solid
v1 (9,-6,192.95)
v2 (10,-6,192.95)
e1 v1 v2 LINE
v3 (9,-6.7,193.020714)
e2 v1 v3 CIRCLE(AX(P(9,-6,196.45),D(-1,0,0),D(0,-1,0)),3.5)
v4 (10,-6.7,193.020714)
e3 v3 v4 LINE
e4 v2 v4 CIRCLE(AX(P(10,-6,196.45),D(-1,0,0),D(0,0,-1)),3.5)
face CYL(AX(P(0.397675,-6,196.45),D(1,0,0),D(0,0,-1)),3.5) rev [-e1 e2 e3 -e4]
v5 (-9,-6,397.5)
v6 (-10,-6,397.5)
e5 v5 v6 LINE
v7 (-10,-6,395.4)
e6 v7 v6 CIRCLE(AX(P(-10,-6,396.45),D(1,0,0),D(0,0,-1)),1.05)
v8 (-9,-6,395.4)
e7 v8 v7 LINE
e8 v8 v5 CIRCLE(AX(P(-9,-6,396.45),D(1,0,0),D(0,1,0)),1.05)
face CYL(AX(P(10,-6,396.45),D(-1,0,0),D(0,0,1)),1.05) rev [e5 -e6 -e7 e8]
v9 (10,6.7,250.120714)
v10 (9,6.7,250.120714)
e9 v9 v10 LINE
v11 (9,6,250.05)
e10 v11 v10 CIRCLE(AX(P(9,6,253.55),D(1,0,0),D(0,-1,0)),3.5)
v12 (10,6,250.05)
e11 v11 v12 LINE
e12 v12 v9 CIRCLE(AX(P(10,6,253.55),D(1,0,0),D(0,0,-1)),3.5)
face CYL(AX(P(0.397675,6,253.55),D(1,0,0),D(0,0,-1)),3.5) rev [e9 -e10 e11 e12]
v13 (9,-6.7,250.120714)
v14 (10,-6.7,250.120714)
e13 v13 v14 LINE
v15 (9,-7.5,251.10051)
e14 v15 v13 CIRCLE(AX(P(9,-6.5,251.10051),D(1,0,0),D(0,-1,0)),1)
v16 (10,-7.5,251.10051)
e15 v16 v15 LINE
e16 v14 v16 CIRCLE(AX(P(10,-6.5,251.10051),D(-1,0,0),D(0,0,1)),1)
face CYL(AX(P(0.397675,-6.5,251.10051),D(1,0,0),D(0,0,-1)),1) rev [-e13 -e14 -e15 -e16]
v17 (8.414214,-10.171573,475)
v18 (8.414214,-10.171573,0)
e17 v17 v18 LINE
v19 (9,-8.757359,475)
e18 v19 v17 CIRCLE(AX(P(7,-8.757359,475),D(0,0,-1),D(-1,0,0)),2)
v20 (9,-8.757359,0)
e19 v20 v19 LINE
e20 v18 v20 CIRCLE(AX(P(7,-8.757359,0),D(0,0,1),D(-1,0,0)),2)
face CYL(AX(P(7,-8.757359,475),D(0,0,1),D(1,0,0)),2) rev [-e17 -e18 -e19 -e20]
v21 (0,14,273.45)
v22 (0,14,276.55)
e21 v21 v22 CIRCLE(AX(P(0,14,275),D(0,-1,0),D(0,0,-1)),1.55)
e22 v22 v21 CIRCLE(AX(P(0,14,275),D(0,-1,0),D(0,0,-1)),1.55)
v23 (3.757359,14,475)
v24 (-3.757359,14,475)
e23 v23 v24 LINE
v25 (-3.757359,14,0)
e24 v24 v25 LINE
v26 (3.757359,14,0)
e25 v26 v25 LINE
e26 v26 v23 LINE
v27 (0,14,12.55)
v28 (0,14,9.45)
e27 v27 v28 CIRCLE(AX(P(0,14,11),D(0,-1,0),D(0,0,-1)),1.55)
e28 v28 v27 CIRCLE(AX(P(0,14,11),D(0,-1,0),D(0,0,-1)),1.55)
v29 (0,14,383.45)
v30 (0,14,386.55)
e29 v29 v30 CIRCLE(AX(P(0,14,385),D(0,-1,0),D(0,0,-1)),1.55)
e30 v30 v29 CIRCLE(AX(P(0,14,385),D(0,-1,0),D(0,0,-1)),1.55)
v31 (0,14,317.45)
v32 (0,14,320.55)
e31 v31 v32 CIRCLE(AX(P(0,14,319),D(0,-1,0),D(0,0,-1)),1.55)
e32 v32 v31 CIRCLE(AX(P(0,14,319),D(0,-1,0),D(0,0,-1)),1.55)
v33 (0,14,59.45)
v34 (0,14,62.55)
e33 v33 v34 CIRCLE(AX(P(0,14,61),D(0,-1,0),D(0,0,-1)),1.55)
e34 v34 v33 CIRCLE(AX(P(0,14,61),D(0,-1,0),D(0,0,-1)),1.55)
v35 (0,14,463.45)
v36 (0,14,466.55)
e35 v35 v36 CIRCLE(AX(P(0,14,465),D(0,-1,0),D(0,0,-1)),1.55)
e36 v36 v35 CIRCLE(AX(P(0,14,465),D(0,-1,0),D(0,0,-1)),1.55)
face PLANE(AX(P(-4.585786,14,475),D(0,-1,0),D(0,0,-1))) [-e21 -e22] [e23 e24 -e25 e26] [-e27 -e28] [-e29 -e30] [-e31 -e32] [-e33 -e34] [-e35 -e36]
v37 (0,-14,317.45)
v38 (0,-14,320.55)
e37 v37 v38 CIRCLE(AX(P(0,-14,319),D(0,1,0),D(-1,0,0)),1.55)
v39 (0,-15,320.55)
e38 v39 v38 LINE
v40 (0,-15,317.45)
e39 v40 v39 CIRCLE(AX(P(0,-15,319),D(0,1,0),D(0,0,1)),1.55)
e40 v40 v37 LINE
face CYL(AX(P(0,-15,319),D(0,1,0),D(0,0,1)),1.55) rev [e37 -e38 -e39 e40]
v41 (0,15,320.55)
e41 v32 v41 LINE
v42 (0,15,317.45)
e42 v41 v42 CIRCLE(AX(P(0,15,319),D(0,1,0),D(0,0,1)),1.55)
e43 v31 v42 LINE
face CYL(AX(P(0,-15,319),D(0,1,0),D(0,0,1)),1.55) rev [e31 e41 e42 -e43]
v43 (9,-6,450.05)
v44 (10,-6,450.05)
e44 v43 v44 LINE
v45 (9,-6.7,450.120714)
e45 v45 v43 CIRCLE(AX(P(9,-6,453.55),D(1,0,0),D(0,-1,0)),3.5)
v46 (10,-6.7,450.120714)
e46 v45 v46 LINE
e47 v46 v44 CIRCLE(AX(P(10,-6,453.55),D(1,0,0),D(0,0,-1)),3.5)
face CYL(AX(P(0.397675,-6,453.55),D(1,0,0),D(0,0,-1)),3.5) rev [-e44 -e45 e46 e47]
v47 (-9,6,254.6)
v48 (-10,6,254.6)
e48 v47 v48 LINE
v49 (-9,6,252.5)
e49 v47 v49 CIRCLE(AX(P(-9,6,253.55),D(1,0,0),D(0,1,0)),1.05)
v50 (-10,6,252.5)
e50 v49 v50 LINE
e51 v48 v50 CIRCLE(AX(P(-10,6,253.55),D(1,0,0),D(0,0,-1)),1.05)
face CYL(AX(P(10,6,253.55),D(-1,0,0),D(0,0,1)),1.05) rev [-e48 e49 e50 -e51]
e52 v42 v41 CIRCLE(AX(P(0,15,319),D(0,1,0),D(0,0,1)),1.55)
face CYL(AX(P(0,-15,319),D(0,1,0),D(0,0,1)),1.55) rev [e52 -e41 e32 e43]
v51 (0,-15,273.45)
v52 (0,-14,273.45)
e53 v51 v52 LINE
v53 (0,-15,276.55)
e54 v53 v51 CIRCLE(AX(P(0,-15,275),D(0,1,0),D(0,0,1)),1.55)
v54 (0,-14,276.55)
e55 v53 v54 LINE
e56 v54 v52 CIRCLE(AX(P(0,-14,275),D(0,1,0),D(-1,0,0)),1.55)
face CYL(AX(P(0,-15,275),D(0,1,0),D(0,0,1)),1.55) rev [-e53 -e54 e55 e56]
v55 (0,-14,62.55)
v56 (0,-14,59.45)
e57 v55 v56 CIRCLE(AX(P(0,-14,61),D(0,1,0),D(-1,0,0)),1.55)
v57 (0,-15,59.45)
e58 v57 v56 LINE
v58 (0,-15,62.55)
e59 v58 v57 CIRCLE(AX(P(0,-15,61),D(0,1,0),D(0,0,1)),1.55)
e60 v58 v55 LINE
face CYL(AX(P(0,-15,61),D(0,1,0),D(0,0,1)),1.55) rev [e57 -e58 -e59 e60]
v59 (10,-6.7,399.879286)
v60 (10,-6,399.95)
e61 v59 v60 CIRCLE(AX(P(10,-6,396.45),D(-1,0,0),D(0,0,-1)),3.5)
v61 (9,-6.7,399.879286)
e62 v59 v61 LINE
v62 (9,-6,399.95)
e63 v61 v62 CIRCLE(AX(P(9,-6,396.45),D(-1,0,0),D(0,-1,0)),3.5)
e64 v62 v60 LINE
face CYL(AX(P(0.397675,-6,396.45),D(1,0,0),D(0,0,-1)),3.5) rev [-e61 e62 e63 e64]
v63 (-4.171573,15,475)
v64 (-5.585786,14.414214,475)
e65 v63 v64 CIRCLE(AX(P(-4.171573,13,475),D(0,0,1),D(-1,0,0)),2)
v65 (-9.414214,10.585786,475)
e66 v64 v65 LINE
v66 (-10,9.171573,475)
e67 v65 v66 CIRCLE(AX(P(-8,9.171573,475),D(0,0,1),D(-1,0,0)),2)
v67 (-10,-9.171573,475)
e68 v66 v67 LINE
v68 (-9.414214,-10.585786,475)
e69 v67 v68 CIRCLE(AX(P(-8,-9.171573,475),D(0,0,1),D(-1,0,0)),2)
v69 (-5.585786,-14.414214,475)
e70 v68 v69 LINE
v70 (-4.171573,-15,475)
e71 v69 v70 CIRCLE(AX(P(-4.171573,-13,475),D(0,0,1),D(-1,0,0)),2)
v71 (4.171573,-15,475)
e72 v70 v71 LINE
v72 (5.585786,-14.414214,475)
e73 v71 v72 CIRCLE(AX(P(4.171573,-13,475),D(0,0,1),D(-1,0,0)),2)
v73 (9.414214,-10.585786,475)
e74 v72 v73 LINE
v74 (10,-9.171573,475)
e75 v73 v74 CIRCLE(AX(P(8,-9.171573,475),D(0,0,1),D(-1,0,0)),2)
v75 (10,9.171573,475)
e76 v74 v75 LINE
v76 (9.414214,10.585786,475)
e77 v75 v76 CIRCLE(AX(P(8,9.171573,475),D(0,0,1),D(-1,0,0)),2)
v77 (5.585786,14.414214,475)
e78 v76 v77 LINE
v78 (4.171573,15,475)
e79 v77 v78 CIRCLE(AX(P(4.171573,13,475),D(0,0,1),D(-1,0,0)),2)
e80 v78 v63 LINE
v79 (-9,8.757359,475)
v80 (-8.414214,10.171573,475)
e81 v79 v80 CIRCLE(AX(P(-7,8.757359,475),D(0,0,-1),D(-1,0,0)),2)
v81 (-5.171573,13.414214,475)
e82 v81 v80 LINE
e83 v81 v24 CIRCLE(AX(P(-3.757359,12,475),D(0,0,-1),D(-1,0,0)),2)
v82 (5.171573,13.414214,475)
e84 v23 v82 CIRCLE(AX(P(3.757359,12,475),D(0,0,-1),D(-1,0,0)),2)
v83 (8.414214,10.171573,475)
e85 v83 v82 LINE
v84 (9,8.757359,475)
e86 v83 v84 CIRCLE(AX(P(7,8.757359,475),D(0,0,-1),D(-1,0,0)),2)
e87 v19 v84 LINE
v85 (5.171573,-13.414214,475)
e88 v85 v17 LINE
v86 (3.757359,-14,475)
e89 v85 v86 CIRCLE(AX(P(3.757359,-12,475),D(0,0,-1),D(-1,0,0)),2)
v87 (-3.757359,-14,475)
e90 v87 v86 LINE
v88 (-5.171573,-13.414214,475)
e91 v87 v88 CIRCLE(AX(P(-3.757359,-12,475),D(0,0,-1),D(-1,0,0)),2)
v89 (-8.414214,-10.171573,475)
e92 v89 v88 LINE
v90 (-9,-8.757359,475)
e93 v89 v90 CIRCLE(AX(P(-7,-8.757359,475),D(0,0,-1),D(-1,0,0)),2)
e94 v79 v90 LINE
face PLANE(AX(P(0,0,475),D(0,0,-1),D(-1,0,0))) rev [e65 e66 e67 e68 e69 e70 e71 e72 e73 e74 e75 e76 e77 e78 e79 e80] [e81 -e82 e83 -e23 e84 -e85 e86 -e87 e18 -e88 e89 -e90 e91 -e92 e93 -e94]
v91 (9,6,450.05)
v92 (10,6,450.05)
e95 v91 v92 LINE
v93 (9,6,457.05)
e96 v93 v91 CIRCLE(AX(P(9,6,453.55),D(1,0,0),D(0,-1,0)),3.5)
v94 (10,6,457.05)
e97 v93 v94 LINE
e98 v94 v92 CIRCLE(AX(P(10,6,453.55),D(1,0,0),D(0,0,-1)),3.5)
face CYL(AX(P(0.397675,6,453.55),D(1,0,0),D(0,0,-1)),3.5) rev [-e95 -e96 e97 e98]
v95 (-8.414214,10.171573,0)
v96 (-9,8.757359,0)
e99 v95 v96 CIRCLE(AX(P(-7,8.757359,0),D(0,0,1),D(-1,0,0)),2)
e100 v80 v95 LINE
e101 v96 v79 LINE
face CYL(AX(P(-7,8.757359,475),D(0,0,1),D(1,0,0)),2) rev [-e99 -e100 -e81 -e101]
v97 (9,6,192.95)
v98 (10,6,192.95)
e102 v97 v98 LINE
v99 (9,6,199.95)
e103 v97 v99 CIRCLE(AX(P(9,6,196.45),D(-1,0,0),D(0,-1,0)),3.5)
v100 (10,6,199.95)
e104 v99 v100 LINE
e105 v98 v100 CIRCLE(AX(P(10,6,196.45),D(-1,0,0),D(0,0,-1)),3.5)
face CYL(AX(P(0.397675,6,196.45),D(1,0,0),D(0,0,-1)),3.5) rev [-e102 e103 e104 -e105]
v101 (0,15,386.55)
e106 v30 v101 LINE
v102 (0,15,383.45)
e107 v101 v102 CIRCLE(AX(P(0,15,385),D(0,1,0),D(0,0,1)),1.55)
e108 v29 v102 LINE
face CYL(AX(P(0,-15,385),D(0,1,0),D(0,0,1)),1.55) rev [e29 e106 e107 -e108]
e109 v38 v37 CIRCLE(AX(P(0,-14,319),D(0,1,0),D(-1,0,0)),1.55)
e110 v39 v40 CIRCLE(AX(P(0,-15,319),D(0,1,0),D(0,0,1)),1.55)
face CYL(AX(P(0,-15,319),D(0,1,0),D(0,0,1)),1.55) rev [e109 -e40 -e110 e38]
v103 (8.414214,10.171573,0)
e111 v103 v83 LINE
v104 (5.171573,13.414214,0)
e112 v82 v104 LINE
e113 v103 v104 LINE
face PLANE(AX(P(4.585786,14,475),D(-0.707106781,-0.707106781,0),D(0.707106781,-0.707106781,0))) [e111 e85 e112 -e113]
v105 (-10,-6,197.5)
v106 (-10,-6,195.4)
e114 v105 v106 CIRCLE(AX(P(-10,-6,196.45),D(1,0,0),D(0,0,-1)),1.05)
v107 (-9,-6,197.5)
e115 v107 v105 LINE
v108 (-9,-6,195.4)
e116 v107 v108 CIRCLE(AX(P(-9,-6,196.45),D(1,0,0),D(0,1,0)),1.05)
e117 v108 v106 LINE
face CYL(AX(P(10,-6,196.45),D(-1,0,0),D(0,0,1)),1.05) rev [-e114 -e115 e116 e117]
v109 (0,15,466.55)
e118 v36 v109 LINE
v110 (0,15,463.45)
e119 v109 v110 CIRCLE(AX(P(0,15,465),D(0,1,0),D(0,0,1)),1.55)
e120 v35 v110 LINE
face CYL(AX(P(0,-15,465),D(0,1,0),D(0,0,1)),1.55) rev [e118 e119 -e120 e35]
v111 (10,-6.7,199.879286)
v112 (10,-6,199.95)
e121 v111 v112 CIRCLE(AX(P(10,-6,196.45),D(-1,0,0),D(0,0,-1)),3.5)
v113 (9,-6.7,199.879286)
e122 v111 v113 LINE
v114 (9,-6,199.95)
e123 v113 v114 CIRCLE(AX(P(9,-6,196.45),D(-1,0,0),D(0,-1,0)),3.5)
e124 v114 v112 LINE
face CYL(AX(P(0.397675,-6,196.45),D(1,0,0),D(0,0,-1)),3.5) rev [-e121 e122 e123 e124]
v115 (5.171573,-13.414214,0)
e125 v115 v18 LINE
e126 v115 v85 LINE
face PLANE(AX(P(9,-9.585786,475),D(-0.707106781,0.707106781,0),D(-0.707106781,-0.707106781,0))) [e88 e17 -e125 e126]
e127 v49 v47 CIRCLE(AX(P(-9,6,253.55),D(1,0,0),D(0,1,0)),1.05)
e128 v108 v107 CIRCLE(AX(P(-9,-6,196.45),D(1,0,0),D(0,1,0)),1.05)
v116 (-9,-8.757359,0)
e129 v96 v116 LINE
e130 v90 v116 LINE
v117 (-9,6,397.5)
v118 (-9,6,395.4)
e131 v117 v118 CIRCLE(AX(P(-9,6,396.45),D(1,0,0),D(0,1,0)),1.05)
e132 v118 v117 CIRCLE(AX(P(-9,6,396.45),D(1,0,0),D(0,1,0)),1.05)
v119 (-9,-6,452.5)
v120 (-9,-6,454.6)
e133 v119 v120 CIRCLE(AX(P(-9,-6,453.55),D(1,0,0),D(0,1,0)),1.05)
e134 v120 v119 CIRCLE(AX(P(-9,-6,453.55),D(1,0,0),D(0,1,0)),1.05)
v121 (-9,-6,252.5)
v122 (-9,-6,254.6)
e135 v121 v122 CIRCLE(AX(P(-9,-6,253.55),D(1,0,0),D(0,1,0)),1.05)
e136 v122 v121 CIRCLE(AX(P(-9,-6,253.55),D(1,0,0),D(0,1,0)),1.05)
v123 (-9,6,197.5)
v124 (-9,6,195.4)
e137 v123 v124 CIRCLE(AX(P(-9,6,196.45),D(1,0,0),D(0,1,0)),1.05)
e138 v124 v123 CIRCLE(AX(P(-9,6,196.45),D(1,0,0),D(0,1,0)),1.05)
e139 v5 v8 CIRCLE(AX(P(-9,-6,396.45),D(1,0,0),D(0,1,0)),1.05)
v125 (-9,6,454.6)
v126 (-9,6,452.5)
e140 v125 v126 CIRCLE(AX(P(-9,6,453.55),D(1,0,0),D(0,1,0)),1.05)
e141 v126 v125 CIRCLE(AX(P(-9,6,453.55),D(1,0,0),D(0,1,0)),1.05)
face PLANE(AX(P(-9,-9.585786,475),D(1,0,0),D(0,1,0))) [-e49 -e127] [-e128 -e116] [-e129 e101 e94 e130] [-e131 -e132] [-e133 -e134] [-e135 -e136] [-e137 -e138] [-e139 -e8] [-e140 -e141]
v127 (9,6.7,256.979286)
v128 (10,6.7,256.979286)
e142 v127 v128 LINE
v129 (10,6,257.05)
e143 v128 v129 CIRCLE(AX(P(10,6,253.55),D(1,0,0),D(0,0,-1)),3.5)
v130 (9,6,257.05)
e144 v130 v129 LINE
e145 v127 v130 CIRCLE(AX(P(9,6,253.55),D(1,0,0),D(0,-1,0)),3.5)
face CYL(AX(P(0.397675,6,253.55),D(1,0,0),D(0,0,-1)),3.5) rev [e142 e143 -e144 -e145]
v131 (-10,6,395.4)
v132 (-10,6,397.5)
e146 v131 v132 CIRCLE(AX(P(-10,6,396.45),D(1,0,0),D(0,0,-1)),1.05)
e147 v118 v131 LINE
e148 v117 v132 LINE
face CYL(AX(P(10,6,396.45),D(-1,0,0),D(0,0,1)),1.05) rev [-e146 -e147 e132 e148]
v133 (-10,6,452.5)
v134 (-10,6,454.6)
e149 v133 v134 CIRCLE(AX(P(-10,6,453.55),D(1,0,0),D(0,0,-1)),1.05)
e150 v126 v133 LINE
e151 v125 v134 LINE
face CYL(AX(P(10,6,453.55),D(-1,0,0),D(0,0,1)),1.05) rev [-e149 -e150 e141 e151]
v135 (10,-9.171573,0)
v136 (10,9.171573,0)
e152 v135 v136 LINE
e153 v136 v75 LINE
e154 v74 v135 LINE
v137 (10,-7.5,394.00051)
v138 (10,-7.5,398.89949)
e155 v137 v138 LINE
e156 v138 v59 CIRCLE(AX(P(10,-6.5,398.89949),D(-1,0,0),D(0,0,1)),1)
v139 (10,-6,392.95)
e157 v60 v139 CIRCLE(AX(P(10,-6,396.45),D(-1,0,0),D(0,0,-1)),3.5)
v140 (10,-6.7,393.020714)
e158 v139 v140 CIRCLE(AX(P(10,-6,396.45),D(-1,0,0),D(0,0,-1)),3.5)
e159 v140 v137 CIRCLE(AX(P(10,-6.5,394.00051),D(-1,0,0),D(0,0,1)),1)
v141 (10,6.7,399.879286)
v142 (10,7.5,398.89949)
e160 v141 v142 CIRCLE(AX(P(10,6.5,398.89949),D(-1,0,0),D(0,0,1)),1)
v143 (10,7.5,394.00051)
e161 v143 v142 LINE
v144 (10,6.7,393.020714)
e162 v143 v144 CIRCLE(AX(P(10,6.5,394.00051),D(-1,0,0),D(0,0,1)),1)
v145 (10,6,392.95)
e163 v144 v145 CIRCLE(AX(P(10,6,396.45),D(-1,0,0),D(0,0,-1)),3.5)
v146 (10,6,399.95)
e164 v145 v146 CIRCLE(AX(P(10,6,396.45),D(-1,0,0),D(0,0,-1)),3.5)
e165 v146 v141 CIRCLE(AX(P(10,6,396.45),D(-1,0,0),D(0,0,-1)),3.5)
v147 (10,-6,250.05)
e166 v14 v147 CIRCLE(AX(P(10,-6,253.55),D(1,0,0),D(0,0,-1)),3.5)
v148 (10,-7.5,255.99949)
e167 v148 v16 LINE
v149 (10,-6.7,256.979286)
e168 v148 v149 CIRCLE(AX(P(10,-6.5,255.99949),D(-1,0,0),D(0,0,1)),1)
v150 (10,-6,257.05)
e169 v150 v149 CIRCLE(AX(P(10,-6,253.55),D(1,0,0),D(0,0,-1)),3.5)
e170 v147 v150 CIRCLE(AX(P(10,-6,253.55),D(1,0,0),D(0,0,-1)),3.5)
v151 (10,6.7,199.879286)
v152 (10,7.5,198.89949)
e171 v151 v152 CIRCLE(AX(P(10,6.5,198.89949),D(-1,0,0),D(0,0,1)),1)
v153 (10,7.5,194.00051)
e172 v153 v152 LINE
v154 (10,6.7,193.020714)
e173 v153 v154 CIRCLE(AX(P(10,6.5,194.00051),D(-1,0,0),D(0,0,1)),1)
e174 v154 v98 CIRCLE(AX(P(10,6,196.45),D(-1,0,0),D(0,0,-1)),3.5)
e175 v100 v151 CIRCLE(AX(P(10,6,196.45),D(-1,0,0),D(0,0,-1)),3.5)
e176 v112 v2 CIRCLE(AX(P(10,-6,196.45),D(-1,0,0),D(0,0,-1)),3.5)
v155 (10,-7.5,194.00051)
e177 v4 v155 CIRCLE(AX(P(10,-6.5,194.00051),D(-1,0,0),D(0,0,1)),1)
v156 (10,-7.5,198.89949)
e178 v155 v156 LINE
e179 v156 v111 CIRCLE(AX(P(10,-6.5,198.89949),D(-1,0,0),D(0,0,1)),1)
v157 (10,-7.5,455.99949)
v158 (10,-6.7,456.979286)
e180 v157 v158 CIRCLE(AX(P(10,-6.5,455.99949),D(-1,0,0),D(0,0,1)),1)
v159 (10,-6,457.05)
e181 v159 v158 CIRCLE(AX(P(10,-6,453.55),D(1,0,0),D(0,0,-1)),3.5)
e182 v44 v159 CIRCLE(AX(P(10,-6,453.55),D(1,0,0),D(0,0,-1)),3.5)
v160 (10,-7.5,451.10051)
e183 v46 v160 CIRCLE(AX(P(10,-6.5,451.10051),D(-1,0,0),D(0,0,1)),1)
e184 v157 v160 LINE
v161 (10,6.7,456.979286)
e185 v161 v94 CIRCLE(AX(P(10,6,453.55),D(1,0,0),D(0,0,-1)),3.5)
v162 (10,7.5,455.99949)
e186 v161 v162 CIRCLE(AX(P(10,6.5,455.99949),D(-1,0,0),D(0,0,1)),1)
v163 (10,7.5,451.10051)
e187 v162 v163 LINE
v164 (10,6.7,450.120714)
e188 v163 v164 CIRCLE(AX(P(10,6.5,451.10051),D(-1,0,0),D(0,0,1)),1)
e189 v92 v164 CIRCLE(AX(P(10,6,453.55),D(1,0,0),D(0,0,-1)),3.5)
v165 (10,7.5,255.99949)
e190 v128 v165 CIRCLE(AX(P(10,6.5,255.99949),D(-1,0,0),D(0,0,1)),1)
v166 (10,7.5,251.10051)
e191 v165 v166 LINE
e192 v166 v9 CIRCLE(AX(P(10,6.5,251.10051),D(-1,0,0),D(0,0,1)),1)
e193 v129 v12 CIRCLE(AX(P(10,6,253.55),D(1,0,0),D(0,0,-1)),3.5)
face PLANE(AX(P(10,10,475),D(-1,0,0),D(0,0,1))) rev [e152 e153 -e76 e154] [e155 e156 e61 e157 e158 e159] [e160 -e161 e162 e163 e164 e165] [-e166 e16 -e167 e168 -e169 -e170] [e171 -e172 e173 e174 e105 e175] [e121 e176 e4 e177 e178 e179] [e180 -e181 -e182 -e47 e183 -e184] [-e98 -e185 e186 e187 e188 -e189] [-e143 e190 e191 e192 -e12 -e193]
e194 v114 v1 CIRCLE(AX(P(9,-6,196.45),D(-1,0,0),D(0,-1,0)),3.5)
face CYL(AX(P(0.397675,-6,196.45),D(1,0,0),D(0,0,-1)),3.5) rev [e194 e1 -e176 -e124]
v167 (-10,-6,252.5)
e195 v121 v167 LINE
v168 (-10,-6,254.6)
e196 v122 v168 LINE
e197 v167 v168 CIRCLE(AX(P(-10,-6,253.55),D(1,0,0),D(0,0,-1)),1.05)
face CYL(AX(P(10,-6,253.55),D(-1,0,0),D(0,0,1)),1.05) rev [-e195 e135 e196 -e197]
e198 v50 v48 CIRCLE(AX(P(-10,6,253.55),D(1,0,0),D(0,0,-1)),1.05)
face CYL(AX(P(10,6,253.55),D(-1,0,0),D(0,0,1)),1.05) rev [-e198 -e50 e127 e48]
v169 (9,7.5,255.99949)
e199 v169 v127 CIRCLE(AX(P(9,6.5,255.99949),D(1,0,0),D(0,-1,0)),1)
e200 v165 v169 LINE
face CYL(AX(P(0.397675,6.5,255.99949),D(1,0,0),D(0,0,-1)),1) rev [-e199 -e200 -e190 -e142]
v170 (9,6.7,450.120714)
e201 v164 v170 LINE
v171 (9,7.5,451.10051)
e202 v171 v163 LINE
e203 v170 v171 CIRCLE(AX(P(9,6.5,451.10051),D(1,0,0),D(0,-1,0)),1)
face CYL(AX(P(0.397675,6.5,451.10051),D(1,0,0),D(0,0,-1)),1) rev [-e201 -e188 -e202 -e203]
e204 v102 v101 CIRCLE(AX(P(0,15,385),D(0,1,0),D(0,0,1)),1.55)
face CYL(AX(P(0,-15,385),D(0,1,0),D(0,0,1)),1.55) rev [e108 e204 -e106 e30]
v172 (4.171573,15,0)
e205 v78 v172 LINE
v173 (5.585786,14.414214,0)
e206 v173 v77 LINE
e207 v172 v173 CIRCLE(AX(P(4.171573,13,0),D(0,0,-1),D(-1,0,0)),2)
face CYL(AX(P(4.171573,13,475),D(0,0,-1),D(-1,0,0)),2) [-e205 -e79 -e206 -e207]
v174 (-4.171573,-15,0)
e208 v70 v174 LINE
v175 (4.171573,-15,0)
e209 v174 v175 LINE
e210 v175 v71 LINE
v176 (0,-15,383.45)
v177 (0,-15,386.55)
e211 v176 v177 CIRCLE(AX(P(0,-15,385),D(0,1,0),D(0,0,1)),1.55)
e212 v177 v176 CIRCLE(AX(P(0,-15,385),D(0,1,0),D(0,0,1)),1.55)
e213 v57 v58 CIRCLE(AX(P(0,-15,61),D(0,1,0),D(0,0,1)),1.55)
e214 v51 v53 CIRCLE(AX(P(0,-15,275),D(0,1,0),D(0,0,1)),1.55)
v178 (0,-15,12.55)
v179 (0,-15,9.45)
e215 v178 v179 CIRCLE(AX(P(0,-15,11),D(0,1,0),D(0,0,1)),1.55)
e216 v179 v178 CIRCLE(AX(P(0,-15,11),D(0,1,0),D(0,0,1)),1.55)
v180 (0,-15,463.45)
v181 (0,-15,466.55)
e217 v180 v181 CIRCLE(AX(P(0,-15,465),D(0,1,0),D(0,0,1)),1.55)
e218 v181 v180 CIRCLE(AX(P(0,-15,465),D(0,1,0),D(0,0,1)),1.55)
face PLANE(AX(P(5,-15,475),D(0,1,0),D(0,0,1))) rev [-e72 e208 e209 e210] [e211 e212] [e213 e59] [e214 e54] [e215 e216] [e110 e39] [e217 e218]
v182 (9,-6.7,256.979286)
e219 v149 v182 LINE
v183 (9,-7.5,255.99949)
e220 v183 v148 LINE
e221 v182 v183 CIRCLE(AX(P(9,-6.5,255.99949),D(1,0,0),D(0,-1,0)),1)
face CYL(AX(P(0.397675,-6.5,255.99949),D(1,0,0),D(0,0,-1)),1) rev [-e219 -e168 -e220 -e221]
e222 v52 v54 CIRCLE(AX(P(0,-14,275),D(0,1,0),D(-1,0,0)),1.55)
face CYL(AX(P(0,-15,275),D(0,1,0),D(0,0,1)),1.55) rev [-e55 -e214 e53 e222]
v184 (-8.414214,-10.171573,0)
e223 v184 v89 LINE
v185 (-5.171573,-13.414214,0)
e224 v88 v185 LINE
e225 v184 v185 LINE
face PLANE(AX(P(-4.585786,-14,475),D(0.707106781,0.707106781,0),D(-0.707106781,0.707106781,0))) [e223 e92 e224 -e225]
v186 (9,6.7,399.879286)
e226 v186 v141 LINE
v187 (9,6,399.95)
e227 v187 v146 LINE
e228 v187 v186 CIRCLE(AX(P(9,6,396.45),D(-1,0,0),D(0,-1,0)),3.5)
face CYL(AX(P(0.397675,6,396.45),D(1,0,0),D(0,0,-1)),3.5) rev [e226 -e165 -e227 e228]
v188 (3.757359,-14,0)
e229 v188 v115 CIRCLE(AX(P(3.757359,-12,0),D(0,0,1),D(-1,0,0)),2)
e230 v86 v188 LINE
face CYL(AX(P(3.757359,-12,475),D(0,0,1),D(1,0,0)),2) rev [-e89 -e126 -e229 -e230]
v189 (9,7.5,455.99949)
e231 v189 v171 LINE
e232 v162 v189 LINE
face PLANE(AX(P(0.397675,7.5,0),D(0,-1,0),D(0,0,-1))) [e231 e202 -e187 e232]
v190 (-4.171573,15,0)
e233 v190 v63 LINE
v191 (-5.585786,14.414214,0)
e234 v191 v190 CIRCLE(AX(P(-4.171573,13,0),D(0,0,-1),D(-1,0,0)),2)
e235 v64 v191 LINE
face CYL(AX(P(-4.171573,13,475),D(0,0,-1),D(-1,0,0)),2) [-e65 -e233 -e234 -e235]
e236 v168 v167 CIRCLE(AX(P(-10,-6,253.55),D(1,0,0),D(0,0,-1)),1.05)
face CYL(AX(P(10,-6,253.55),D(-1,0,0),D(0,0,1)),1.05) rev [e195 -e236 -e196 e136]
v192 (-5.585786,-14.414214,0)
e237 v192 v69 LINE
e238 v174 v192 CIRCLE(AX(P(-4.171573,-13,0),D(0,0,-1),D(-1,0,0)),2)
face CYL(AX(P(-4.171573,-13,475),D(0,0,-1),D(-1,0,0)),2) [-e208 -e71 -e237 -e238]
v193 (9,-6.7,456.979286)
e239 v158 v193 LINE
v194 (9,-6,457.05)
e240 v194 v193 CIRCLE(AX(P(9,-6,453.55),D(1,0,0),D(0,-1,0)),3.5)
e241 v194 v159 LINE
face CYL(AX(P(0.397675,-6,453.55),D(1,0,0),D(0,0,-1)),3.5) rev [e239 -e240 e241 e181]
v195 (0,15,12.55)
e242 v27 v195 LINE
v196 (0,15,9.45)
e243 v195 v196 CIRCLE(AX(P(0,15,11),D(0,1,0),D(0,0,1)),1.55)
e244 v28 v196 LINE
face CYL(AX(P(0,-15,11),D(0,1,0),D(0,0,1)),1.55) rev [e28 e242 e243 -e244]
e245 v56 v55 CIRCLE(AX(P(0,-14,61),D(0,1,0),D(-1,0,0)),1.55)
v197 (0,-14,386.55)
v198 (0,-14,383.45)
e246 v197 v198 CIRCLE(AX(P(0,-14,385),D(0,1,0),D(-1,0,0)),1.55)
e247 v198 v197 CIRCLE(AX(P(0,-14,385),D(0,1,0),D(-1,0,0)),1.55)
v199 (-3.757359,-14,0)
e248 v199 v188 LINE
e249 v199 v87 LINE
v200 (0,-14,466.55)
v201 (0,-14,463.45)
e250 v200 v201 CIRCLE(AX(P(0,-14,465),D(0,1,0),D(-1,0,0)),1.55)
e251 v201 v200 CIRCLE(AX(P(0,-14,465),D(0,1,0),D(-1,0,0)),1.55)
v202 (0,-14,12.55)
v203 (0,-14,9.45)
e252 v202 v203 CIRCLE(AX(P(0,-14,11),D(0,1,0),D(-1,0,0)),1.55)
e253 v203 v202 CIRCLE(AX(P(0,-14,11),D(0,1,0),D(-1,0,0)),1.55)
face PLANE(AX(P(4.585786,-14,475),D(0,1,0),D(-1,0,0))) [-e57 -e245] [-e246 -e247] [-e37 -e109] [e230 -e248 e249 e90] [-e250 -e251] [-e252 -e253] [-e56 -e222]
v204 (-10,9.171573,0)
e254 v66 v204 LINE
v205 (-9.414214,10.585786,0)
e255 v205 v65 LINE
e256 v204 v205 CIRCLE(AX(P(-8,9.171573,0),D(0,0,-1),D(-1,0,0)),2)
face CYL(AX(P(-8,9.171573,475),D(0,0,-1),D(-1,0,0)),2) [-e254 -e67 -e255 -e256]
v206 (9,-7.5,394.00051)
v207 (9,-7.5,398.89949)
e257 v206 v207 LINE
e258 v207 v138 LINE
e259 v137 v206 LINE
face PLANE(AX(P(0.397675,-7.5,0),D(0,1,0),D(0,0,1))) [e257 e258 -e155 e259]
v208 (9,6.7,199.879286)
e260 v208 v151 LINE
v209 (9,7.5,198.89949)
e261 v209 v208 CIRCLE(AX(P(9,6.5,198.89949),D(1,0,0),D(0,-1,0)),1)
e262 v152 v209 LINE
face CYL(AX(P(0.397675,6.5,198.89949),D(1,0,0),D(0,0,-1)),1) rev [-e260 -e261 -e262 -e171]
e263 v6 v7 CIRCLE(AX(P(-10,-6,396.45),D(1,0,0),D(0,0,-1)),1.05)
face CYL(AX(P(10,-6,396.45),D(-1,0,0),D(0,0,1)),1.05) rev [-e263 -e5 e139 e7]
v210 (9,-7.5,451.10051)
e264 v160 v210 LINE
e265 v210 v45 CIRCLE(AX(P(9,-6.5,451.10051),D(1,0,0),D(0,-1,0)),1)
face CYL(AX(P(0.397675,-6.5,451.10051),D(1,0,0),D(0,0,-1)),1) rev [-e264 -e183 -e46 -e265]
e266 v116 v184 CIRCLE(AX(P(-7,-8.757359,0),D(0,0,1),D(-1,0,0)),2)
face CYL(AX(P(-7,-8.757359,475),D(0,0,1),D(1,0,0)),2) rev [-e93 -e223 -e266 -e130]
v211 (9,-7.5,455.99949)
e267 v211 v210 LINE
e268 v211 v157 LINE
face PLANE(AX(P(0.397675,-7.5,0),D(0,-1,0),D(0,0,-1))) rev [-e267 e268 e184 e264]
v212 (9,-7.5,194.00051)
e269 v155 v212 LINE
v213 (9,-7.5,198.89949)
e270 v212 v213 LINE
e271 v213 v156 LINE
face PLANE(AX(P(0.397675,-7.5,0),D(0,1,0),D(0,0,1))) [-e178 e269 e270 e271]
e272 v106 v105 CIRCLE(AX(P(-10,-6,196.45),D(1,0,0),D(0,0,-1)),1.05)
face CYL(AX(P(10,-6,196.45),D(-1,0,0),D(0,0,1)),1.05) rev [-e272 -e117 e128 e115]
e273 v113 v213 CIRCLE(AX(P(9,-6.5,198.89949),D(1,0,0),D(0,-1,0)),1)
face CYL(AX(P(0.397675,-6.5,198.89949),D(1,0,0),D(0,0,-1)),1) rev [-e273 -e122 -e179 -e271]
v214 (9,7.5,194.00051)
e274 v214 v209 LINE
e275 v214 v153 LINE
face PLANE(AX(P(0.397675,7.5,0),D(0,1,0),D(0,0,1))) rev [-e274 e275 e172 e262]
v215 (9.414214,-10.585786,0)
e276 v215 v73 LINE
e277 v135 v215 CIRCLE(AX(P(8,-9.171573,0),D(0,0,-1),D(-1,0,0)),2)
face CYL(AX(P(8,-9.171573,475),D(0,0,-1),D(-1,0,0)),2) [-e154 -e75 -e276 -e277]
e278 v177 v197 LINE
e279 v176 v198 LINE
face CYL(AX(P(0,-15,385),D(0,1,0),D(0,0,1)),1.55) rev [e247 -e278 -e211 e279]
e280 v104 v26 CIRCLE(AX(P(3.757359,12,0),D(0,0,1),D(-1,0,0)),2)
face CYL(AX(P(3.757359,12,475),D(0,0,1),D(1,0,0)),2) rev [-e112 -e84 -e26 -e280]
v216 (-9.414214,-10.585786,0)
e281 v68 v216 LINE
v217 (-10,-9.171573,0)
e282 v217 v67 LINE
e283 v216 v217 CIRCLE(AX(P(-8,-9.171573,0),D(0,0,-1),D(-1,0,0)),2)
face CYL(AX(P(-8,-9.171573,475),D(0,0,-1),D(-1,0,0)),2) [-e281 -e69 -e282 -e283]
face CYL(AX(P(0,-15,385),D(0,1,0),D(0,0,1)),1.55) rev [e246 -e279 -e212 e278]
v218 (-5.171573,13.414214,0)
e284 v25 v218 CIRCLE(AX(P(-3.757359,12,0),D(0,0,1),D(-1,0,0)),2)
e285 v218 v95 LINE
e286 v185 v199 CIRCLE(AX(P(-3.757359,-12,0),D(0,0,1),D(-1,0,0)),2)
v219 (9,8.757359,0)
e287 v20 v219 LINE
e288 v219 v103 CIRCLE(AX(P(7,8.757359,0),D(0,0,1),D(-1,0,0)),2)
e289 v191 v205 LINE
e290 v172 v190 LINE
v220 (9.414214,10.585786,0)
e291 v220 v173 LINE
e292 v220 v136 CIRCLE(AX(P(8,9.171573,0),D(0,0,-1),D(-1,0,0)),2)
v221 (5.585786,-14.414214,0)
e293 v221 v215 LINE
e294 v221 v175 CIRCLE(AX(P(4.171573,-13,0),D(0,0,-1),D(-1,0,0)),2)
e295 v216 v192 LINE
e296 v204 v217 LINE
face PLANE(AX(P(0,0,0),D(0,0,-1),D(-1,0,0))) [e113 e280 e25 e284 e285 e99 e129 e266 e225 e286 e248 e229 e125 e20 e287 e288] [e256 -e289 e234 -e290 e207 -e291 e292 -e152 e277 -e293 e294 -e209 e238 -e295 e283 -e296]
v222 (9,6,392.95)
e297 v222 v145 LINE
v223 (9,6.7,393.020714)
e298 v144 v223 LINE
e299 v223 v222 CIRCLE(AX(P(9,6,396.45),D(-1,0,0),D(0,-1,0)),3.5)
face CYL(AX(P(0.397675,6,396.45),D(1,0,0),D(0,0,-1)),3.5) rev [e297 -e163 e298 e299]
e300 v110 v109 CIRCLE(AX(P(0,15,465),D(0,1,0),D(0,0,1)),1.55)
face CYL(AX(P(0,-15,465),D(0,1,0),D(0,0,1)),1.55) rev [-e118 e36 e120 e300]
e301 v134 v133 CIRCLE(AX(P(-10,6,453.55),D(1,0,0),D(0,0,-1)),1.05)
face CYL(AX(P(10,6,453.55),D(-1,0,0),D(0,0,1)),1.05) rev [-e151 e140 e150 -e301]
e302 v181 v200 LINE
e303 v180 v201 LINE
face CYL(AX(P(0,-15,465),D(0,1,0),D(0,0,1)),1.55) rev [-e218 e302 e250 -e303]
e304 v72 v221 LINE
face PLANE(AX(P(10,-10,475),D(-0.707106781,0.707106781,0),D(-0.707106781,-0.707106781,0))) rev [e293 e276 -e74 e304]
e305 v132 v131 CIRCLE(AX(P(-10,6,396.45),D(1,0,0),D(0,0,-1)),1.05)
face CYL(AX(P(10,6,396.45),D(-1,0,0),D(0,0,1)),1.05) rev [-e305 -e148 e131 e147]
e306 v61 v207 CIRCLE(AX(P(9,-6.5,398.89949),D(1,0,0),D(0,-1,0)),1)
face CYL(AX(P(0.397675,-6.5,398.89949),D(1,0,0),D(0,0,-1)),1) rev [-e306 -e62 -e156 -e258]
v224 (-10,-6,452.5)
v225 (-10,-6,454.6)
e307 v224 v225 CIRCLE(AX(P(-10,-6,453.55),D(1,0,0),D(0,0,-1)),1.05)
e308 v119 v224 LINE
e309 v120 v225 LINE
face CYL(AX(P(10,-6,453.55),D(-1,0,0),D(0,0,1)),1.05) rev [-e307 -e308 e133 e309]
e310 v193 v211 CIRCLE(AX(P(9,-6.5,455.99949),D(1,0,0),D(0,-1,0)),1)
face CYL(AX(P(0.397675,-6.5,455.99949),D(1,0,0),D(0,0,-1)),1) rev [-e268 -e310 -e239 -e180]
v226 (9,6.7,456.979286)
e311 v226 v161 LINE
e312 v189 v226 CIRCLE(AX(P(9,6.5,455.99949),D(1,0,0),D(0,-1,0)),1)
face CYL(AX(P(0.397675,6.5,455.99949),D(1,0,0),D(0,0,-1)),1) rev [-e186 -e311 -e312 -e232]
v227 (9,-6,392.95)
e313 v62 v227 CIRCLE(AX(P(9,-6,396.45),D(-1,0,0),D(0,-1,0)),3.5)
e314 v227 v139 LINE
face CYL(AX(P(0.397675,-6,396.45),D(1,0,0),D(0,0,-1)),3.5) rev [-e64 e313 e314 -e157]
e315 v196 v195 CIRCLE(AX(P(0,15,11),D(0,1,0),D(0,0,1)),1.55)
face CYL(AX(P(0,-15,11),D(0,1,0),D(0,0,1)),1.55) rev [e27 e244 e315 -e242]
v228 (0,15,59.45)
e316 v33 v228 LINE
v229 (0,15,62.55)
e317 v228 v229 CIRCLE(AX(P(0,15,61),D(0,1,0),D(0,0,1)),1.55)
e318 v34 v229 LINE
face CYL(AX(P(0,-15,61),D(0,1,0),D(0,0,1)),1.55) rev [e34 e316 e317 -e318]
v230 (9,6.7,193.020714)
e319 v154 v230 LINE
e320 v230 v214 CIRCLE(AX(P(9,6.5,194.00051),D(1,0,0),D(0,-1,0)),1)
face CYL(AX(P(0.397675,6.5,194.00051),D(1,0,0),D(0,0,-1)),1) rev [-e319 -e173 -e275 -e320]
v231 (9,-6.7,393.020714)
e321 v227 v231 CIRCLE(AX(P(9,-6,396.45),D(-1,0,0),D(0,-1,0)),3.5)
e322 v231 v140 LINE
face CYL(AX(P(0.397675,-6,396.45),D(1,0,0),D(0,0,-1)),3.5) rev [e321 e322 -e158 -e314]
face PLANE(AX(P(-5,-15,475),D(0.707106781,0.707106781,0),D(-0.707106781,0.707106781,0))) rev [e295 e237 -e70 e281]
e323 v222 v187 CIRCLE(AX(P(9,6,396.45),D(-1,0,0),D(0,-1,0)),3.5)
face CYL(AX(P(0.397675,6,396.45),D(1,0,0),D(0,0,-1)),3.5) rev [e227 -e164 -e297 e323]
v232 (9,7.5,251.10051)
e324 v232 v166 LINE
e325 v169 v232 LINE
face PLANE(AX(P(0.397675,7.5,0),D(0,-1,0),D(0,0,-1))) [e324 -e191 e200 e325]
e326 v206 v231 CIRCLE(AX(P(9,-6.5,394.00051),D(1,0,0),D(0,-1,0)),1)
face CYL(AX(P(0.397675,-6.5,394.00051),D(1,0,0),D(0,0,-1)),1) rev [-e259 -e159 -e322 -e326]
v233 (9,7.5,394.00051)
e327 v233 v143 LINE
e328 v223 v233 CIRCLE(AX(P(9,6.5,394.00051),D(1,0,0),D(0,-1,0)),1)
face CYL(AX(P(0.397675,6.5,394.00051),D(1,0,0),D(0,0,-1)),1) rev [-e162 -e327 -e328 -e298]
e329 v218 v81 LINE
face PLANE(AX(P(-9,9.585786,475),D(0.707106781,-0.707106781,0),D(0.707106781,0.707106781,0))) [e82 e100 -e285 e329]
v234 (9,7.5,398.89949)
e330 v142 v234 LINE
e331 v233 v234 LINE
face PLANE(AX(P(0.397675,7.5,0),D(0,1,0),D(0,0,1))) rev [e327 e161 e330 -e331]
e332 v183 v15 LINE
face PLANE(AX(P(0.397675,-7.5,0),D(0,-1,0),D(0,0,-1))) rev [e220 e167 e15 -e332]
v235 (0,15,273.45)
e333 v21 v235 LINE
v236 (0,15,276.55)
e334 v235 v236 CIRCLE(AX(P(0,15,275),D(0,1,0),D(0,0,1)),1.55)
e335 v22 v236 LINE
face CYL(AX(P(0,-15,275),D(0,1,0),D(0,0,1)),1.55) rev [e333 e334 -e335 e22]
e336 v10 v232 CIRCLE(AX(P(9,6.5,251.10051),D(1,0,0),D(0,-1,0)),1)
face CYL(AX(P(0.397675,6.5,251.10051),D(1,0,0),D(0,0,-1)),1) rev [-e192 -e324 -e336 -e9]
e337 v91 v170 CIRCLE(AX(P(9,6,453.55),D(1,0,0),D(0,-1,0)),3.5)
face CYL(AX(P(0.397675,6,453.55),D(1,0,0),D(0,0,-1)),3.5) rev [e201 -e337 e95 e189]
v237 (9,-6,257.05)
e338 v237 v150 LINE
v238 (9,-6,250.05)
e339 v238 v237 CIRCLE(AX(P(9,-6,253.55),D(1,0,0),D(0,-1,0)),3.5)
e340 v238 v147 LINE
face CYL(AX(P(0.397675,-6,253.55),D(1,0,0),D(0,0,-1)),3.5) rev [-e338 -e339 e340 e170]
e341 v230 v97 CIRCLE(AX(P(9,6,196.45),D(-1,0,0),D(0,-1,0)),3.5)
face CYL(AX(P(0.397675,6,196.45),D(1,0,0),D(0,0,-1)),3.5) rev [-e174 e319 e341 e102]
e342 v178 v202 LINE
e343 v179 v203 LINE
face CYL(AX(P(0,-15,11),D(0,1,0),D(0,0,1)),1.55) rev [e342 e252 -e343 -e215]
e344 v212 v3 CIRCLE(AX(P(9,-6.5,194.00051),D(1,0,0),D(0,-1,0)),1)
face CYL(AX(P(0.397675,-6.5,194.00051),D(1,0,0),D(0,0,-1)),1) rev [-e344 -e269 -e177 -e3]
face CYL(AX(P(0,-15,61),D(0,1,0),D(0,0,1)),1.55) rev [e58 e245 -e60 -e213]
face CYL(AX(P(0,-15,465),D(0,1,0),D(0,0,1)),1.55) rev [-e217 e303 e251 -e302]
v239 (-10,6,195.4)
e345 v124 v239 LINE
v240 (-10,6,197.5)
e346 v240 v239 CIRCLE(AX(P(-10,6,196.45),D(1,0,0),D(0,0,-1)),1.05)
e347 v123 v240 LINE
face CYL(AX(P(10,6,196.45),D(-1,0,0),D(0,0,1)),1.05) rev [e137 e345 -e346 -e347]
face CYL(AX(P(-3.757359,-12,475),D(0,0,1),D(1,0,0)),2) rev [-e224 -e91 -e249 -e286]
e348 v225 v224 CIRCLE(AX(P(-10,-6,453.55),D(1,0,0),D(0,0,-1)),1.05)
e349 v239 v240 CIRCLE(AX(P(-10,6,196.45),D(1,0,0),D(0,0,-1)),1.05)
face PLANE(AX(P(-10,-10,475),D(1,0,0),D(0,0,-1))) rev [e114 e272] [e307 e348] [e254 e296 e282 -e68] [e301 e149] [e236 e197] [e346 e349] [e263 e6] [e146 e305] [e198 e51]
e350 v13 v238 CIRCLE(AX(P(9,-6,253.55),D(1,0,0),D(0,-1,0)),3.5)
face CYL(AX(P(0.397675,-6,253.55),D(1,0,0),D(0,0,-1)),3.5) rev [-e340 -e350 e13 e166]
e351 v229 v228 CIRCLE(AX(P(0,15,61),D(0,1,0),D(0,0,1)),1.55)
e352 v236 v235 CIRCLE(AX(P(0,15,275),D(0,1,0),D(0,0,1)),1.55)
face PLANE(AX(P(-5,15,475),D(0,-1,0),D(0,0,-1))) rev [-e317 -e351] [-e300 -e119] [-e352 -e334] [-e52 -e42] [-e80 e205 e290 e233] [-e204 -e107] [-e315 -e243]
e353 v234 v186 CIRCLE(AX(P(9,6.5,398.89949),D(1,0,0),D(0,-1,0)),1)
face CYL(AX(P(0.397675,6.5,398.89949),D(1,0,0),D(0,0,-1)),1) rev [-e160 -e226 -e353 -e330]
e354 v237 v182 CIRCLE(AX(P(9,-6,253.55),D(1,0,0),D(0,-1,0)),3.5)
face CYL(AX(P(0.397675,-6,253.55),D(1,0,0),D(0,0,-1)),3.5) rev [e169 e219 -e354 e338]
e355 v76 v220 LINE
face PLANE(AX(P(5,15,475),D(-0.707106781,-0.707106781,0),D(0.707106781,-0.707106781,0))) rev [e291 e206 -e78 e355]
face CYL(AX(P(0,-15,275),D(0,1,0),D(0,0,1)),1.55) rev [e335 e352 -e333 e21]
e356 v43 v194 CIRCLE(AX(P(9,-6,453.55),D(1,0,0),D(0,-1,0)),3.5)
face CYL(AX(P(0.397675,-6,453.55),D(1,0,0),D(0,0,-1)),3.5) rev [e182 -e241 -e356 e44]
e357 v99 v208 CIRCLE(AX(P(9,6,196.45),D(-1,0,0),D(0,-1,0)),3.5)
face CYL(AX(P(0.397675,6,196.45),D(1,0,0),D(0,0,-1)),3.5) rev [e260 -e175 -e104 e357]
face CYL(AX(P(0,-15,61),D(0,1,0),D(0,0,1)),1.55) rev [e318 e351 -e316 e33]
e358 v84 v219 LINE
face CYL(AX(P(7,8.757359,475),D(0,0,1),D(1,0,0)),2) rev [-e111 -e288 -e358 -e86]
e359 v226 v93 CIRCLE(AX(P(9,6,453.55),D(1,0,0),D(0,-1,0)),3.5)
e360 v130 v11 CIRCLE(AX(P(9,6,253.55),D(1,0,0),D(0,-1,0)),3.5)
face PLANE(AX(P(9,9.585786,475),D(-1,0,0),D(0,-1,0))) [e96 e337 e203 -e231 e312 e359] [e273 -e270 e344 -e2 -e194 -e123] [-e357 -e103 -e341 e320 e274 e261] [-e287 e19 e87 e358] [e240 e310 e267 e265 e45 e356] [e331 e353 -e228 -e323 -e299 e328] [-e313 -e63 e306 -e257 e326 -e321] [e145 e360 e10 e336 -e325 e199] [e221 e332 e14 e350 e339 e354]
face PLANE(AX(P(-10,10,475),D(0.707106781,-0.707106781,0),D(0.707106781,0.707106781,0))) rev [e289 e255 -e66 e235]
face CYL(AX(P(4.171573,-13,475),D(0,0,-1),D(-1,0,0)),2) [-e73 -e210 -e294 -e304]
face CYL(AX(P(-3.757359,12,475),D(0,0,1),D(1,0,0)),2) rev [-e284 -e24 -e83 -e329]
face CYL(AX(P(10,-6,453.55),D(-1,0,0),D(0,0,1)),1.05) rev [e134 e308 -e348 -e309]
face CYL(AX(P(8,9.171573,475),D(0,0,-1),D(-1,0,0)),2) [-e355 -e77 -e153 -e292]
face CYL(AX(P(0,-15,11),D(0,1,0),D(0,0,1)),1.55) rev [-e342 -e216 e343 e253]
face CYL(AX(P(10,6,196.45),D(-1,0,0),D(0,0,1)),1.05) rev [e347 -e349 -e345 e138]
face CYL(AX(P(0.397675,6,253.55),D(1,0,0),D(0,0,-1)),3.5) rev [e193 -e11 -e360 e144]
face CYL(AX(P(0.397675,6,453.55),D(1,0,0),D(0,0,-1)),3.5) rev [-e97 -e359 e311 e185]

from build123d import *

# Parameters (mm, degrees)
EXTRUDE_1_DEPTH          = 475
FILLET_1_R               = 2
SKETCH_2_R               = 1.55
CUT_EXTRUDE_1_DEPTH      = 477.051467806
CUT_EXTRUDE_2_DEPTH      = 476.657439761
CUT_EXTRUDE_2_DEPTH_BACK = 476.657439761
SKETCH_3_R               = 1.05
CUT_EXTRUDE_START        = -1
SKETCH_4_R               = 1.05
CUT_EXTRUDE_3_DEPTH      = 1
FILLET_2_R               = 1


with BuildPart() as part:
    # 草图1 → 凸台-拉伸1 (new body)
    with BuildSketch(Plane.XY):
        Polygon((-5, 15), (5, 15), (10, 10), (10, -10), (5, -15), (-5, -15), (-10, -10), (-10, 10), align=None)
        Polygon((-9, 9.585786438), (-4.585786438, 14), (4.585786438, 14), (9, 9.585786438), (9, -9.585786438), (4.585786438, -14), (-4.585786438, -14), (-9, -9.585786438), align=None, mode=Mode.SUBTRACT)
    extrude(amount=EXTRUDE_1_DEPTH)

    # 圆角1
    fillet_1_edges = [part.edges().sort_by_distance(p)[0] for p in [
        (-5, 15, 237.5),
        (5, 15, 237.5),
        (10, 10, 237.5),
        (10, -10, 237.5),
        (5, -15, 237.5),
        (-5, -15, 237.5),
        (-10, -10, 237.5),
        (-10, 10, 237.5),
        (-9, 9.585786438, 237.5),
        (-9, -9.585786438, 237.5),
        (-4.585786438, -14, 237.5),
        (4.585786438, -14, 237.5),
        (9, -9.585786438, 237.5),
        (9, 9.585786438, 237.5),
        (4.585786438, 14, 237.5),
        (-4.585786438, 14, 237.5),
    ]]
    fillet(fillet_1_edges, radius=FILLET_1_R)

    # 草图2 → 切除-拉伸1 (cut, through all)
    with BuildSketch(Plane(origin=(0, 15, 0), x_dir=(1, 0, 0), z_dir=(0, 1, 0))):
        with Locations(Location((0, -11, 0), (0, 0, 270))):
            Circle(SKETCH_2_R)
        with Locations(Location((0, -61, 0), (0, 0, 270))):
            Circle(SKETCH_2_R)
        with Locations(Location((0, -385, 0), (0, 0, 270))):
            Circle(SKETCH_2_R)
        with Locations(Location((0, -465, 0), (0, 0, 270))):
            Circle(SKETCH_2_R)
        with Locations(Location((0, -319, 0), (0, 0, 270))):
            Circle(SKETCH_2_R)
        with Locations(Location((0, -275, 0), (0, 0, 270))):
            Circle(SKETCH_2_R)
    extrude(amount=-CUT_EXTRUDE_1_DEPTH, mode=Mode.SUBTRACT)

    # 草图3 → 切除-拉伸2 (cut, two sides: drawn at the far end of the back side and taken through both)
    with BuildSketch(Plane.ZY.offset(10).offset(-CUT_EXTRUDE_2_DEPTH_BACK)):
        with Locations((396.45, 6)):
            Circle(SKETCH_3_R)
        with Locations((396.45, -6)):
            Circle(SKETCH_3_R)
        with Locations((453.55, 6)):
            Circle(SKETCH_3_R)
        with Locations((453.55, -6)):
            Circle(SKETCH_3_R)
        with Locations((196.45, 6)):
            Circle(SKETCH_3_R)
        with Locations((196.45, -6)):
            Circle(SKETCH_3_R)
        with Locations((253.55, 6)):
            Circle(SKETCH_3_R)
        with Locations((253.55, -6)):
            Circle(SKETCH_3_R)
    extrude(amount=CUT_EXTRUDE_2_DEPTH + CUT_EXTRUDE_2_DEPTH_BACK, mode=Mode.SUBTRACT)

    # 草图4 → 切除-拉伸3 (cut)
    # profile 1 of 8: a face of its own
    with BuildSketch(Plane(origin=(10, 0, 0), x_dir=(0, 0, -1), z_dir=(1, 0, 0)).offset(CUT_EXTRUDE_START)):
        with BuildLine():
            Line((-450.38772234, 7.5), (-456.71227766, 7.5))
            ThreePointArc((-456.71227766, 7.5), (-454.318774411, 2.585474278), (-450.05, 6))
            ThreePointArc((-450.05, 6), (-450.135474278, 6.768774411), (-450.38772234, 7.5))
        make_face()
        with Locations(Location((-453.55, 6, 0), (0, 0, 180))):
            Circle(SKETCH_4_R, mode=Mode.SUBTRACT)
    # profile 2 of 8: a face of its own
    with BuildSketch(Plane(origin=(10, 0, 0), x_dir=(0, 0, -1), z_dir=(1, 0, 0)).offset(CUT_EXTRUDE_START)):
        with BuildLine():
            ThreePointArc((-450.05, -6), (-454.318774411, -2.585474278), (-456.71227766, -7.5))
            Line((-456.71227766, -7.5), (-450.38772234, -7.5))
            ThreePointArc((-450.38772234, -7.5), (-450.135474278, -6.768774411), (-450.05, -6))
        make_face()
        with Locations(Location((-453.55, -6, 0), (0, 0, 180))):
            Circle(SKETCH_4_R, mode=Mode.SUBTRACT)
    # profile 3 of 8: a face of its own
    with BuildSketch(Plane(origin=(10, 0, 0), x_dir=(0, 0, -1), z_dir=(1, 0, 0)).offset(CUT_EXTRUDE_START)):
        with BuildLine():
            Line((-399.61227766, -7.5), (-393.28772234, -7.5))
            ThreePointArc((-393.28772234, -7.5), (-393.035474278, -6.768774411), (-392.95, -6))
            ThreePointArc((-392.95, -6), (-397.218774411, -2.585474278), (-399.61227766, -7.5))
        make_face()
        with Locations(Location((-396.45, -6, 0), (0, 0, 180))):
            Circle(SKETCH_4_R, mode=Mode.SUBTRACT)
    # profile 4 of 8: a face of its own
    with BuildSketch(Plane(origin=(10, 0, 0), x_dir=(0, 0, -1), z_dir=(1, 0, 0)).offset(CUT_EXTRUDE_START)):
        with BuildLine():
            ThreePointArc((-392.95, 6), (-393.035474278, 6.768774411), (-393.28772234, 7.5))
            Line((-393.28772234, 7.5), (-399.61227766, 7.5))
            ThreePointArc((-399.61227766, 7.5), (-397.218774411, 2.585474278), (-392.95, 6))
        make_face()
        with Locations(Location((-396.45, 6, 0), (0, 0, 180))):
            Circle(SKETCH_4_R, mode=Mode.SUBTRACT)
    # profile 5 of 8: a face of its own
    with BuildSketch(Plane(origin=(10, 0, 0), x_dir=(0, 0, -1), z_dir=(1, 0, 0)).offset(CUT_EXTRUDE_START)):
        with BuildLine():
            Line((-250.38772234, 7.5), (-256.71227766, 7.5))
            ThreePointArc((-256.71227766, 7.5), (-254.318774411, 2.585474278), (-250.05, 6))
            ThreePointArc((-250.05, 6), (-250.135474278, 6.768774411), (-250.38772234, 7.5))
        make_face()
        with Locations(Location((-253.55, 6, 0), (0, 0, 180))):
            Circle(SKETCH_4_R, mode=Mode.SUBTRACT)
    # profile 6 of 8: a face of its own
    with BuildSketch(Plane(origin=(10, 0, 0), x_dir=(0, 0, -1), z_dir=(1, 0, 0)).offset(CUT_EXTRUDE_START)):
        with BuildLine():
            ThreePointArc((-250.05, -6), (-254.318774411, -2.585474278), (-256.71227766, -7.5))
            Line((-256.71227766, -7.5), (-250.38772234, -7.5))
            ThreePointArc((-250.38772234, -7.5), (-250.135474278, -6.768774411), (-250.05, -6))
        make_face()
        with Locations(Location((-253.55, -6, 0), (0, 0, 180))):
            Circle(SKETCH_4_R, mode=Mode.SUBTRACT)
    # profile 7 of 8: a face of its own
    with BuildSketch(Plane(origin=(10, 0, 0), x_dir=(0, 0, -1), z_dir=(1, 0, 0)).offset(CUT_EXTRUDE_START)):
        with BuildLine():
            ThreePointArc((-192.95, 6), (-193.035474278, 6.768774411), (-193.28772234, 7.5))
            Line((-193.28772234, 7.5), (-199.61227766, 7.5))
            ThreePointArc((-199.61227766, 7.5), (-197.218774411, 2.585474278), (-192.95, 6))
        make_face()
        with Locations(Location((-196.45, 6, 0), (0, 0, 180))):
            Circle(SKETCH_4_R, mode=Mode.SUBTRACT)
    # profile 8 of 8: a face of its own
    with BuildSketch(Plane(origin=(10, 0, 0), x_dir=(0, 0, -1), z_dir=(1, 0, 0)).offset(CUT_EXTRUDE_START)):
        with BuildLine():
            Line((-199.61227766, -7.5), (-193.28772234, -7.5))
            ThreePointArc((-193.28772234, -7.5), (-193.035474278, -6.768774411), (-192.95, -6))
            ThreePointArc((-192.95, -6), (-197.218774411, -2.585474278), (-199.61227766, -7.5))
        make_face()
        with Locations(Location((-196.45, -6, 0), (0, 0, 180))):
            Circle(SKETCH_4_R, mode=Mode.SUBTRACT)
    extrude(amount=CUT_EXTRUDE_3_DEPTH, mode=Mode.SUBTRACT)

    # 圆角2
    fillet_2_edges = [part.edges().sort_by_distance(p)[0] for p in [
        (9.5, -7.5, 456.71227766),
        (9.5, -7.5, 450.38772234),
        (9.5, -7.5, 393.28772234),
        (9.5, -7.5, 399.61227766),
        (9.5, 7.5, 399.61227766),
        (9.5, 7.5, 393.28772234),
        (9.5, 7.5, 250.38772234),
        (9.5, 7.5, 256.71227766),
        (9.5, -7.5, 193.28772234),
        (9.5, -7.5, 199.61227766),
        (9.5, 7.5, 199.61227766),
        (9.5, 7.5, 193.28772234),
        (9.5, -7.5, 256.71227766),
        (9.5, -7.5, 250.38772234),
        (9.5, 7.5, 450.38772234),
        (9.5, 7.5, 456.71227766),
    ]]
    fillet(fillet_2_edges, radius=FILLET_2_R)


solid = part.part
